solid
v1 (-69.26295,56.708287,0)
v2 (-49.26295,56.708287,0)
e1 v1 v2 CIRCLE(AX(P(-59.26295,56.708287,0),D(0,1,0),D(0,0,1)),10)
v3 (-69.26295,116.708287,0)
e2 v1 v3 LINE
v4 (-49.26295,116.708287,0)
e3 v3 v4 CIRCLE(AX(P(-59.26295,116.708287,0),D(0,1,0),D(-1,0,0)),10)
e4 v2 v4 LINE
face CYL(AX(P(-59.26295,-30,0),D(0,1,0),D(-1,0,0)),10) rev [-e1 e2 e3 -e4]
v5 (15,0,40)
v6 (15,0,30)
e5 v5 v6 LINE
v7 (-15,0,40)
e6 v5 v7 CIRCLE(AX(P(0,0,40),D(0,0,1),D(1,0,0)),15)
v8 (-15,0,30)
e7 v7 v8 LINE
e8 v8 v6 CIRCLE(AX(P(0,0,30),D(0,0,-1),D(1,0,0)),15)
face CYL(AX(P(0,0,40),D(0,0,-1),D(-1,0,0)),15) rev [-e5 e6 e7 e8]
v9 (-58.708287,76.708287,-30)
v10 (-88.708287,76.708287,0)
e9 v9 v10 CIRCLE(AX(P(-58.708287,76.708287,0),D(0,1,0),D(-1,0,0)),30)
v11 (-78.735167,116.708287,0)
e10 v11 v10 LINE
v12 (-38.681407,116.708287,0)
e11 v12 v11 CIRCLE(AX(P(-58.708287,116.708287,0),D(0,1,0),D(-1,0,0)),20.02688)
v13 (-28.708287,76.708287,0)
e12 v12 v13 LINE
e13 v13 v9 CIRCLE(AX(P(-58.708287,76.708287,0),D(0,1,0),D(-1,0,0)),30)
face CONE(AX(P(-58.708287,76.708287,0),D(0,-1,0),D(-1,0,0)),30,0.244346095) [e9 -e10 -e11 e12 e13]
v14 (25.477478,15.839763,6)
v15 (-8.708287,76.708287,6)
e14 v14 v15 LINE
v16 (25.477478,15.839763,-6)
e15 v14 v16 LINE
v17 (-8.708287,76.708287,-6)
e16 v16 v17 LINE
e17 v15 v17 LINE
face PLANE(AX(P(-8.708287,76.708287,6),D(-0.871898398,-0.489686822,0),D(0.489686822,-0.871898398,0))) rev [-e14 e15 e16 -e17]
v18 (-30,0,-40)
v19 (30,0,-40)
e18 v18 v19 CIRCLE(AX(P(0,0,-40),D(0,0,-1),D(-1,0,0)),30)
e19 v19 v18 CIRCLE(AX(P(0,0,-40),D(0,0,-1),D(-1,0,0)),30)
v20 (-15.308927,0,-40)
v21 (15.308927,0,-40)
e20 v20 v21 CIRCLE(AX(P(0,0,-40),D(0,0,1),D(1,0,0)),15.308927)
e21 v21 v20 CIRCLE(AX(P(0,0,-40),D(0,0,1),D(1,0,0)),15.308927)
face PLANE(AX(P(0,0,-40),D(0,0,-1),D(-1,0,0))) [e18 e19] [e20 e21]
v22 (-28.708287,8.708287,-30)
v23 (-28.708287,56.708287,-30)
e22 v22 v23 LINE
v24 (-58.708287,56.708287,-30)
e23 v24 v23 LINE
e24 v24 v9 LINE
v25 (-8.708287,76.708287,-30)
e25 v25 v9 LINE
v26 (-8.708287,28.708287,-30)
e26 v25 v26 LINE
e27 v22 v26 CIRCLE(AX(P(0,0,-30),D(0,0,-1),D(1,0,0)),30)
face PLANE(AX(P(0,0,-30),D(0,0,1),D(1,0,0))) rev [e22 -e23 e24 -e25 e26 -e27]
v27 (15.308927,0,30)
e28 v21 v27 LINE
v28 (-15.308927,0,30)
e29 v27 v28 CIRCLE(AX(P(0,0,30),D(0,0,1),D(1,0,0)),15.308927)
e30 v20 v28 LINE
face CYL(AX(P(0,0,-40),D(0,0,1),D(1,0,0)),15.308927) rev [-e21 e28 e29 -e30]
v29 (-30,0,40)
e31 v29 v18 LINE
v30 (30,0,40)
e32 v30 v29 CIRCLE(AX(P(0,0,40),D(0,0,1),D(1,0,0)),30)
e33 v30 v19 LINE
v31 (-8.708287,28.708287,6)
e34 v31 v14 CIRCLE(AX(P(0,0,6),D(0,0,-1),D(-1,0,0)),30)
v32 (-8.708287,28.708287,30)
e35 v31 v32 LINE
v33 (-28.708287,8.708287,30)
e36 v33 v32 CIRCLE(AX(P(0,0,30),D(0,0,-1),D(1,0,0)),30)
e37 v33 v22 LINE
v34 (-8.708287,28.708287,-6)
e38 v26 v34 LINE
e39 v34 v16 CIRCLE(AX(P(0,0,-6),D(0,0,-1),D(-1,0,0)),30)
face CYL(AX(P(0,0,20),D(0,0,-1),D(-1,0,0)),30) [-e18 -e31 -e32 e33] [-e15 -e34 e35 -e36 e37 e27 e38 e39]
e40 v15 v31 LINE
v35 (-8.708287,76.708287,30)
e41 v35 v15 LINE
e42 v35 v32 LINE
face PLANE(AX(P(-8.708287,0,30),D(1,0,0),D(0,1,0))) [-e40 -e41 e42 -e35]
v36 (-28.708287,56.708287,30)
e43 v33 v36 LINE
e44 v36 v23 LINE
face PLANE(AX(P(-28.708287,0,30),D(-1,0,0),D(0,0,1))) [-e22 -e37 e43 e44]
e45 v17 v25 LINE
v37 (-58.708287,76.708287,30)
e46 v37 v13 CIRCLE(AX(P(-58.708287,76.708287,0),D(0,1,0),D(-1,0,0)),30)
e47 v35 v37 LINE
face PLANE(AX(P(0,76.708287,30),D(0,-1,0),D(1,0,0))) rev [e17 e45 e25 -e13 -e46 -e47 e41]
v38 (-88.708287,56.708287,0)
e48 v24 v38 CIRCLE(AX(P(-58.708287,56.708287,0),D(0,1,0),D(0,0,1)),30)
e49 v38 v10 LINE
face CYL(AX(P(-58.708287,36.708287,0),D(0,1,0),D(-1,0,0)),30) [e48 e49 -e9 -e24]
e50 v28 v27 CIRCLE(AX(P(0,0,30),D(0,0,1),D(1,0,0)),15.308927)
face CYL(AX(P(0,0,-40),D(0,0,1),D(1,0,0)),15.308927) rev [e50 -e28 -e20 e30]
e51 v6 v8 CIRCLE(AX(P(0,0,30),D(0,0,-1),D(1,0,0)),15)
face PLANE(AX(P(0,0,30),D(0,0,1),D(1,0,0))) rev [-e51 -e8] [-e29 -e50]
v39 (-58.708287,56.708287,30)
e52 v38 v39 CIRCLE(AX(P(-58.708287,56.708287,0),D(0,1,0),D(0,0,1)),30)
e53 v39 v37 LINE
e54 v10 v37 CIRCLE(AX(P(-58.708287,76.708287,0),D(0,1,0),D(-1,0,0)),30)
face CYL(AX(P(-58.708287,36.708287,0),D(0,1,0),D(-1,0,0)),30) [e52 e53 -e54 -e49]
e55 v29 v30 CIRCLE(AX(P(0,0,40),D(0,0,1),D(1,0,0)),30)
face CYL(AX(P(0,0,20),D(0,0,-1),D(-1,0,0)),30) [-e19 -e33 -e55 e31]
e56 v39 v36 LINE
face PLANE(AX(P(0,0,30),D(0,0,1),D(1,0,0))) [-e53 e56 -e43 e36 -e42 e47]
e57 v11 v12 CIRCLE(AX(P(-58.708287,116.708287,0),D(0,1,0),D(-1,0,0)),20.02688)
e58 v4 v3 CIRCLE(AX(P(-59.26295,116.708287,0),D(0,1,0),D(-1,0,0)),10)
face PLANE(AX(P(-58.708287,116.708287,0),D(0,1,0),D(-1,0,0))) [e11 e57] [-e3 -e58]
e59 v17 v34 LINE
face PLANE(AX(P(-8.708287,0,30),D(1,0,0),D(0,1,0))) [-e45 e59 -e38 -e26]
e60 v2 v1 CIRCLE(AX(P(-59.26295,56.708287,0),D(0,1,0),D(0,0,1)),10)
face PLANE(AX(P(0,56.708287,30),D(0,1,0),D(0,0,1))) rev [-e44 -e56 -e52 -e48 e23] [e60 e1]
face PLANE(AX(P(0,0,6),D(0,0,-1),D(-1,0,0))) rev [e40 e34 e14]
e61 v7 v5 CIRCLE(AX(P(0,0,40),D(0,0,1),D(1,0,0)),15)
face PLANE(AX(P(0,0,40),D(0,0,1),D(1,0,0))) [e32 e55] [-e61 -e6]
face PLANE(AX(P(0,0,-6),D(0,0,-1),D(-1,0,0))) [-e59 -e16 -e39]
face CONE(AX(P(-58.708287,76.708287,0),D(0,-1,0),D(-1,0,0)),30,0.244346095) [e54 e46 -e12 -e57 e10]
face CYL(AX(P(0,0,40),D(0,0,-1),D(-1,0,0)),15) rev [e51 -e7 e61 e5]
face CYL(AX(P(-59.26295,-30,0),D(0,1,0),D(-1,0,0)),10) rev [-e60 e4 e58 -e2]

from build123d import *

# Parameters (mm, degrees)
BASE_CYLINDER_SKETCH_R         = 30
BASE_CYLINDER_SKETCH_R_2       = 15
BASE_CYLINDER_60_DEPTH         = 20
SUPPORT_ARM_DEPTH              = 30
HUB_BOSS_A_SKETCH_R            = 30
HUB_BOSS_A_DEPTH               = 10
HUB_BOSS_B_SKETCH_R            = 30
HUB_BOSS_B_DEPTH               = 10
ARM_PAD_SKETCH_R               = 30
ARM_PAD_SKETCH_R_2             = 15
ARM_PAD_DEPTH                  = 10
ARM_BOSS_SKETCH_R              = 30
ARM_BOSS_DEPTH                 = 10
SUPPORT_RIB_12MM_DEPTH         = 6
ARM_POCKET_CUT_DEPTH           = 40
TAPERED_BOSS_SKETCH_R          = 30
TAPERED_BOSS_14DEG_DRAFT_DEPTH = 40
TAPERED_BOSS_14DEG_DRAFT_TAPER = 14
BOSS_HOLE_SKETCH_R             = 10
BOSS_HOLE_20_DEPTH             = 177.046816624
CYLINDER_BORE_SKETCH_R         = 15.308926848
CYLINDER_BORE_DEPTH            = 163.449944447


with BuildPart() as part:
    # Base Cylinder Sketch → Base Cylinder Ø60 (new, symmetric)
    with BuildSketch(Plane.XY):
        Circle(BASE_CYLINDER_SKETCH_R)
        Circle(BASE_CYLINDER_SKETCH_R_2, mode=Mode.SUBTRACT)
    extrude(amount=BASE_CYLINDER_60_DEPTH, both=True)

    # Support Arm Sketch → Support Arm (add, symmetric)
    with BuildSketch(Plane.XY):
        with BuildLine():
            Line((-28.708286934, 56.708286934), (-28.708286934, 8.708286934))
            ThreePointArc((-28.708286934, 8.708286934), (-21.213203436, 21.213203436), (-8.708286934, 28.708286934))
            Line((-8.708286934, 28.708286934), (-8.708286934, 76.708286934))
            Line((-8.708286934, 76.708286934), (-88.708286934, 76.708286934))
            Line((-88.708286934, 76.708286934), (-88.708286934, 56.708286934))
            Line((-88.708286934, 56.708286934), (-28.708286934, 56.708286934))
        make_face()
    extrude(amount=SUPPORT_ARM_DEPTH, both=True)

    # Hub Boss A Sketch → Hub Boss A (add, symmetric)
    with BuildSketch(Plane.XY.offset(20)):
        Circle(HUB_BOSS_A_SKETCH_R)
    extrude(amount=HUB_BOSS_A_DEPTH, both=True)

    # Hub Boss B Sketch → Hub Boss B (add, symmetric)
    with BuildSketch(Plane(origin=(0, 0, -20), x_dir=(-1, 0, 0), z_dir=(0, 0, -1))):
        Circle(HUB_BOSS_B_SKETCH_R)
    extrude(amount=HUB_BOSS_B_DEPTH, both=True)

    # Arm Pad Sketch → Arm Pad (add, symmetric)
    with BuildSketch(Plane.XY.offset(30)):
        with Locations(Location((0, 0, 0), (0, 0, 163.125505702))):
            Circle(ARM_PAD_SKETCH_R)
        Circle(ARM_PAD_SKETCH_R_2, mode=Mode.SUBTRACT)
    extrude(amount=ARM_PAD_DEPTH, both=True)

    # Arm Boss Sketch → Arm Boss (add, symmetric)
    with BuildSketch(Plane(origin=(0, 0, -30), x_dir=(-1, 0, 0), z_dir=(0, 0, -1))):
        Circle(ARM_BOSS_SKETCH_R)
    extrude(amount=ARM_BOSS_DEPTH, both=True)

    # Rib Profile Sketch → Support Rib 12mm (add, symmetric)
    with BuildSketch(Plane.XY):
        with BuildLine():
            Line((-8.708286934, 76.708286934), (-8.708286934, 28.708286934))
            ThreePointArc((-8.708286934, 28.708286934), (10.568877445, 28.076659872), (25.477478309, 15.839763225))
            Line((25.477478309, 15.839763225), (-8.708286934, 76.708286934))
        make_face()
    extrude(amount=SUPPORT_RIB_12MM_DEPTH, both=True)

    # Arm Pocket Sketch → Arm Pocket Cut (cut)
    with BuildSketch(Plane(origin=(0, 76.708286934, 0), x_dir=(1, 0, 0), z_dir=(0, 1, 0))):
        with BuildLine():
            Line((-88.708286934, -30), (-58.708286934, -30))
            ThreePointArc((-58.708286934, -30), (-79.921490343, -21.213203462), (-88.708286934, -7.5e-08))
            Line((-88.708286934, -7.5e-08), (-88.708286934, -30))
        make_face()
        with BuildLine():
            Line((-88.708286934, 30), (-88.708286934, -7.5e-08))
            ThreePointArc((-88.708286934, -7.5e-08), (-79.921490396, 21.213203409), (-58.708286934, 30))
            Line((-58.708286934, 30), (-88.708286934, 30))
        make_face()
    extrude(amount=-ARM_POCKET_CUT_DEPTH, mode=Mode.SUBTRACT)

    # Tapered Boss Sketch → Tapered Boss 14deg Draft (add)
    with BuildSketch(Plane(origin=(0, 76.708286934, 0), x_dir=(1, 0, 0), z_dir=(0, 1, 0))):
        with Locations((-58.708286934, 0)):
            Circle(TAPERED_BOSS_SKETCH_R)
    extrude(amount=TAPERED_BOSS_14DEG_DRAFT_DEPTH, taper=TAPERED_BOSS_14DEG_DRAFT_TAPER)

    # Boss Hole Sketch → Boss Hole Ø20 (cut, through all)
    with BuildSketch(Plane(origin=(0, 116.708286934, 0), x_dir=(1, 0, 0), z_dir=(0, 1, 0))):
        with Locations(Location((-59.262949737, 0, 0), (0, 0, 180))):
            Circle(BOSS_HOLE_SKETCH_R)
    extrude(amount=-BOSS_HOLE_20_DEPTH, mode=Mode.SUBTRACT)

    # Cylinder Bore Sketch → Cylinder Bore (cut, through all)
    with BuildSketch(Plane.XY.offset(30)):
        Circle(CYLINDER_BORE_SKETCH_R)
    extrude(amount=-CYLINDER_BORE_DEPTH, mode=Mode.SUBTRACT)


solid = part.part
